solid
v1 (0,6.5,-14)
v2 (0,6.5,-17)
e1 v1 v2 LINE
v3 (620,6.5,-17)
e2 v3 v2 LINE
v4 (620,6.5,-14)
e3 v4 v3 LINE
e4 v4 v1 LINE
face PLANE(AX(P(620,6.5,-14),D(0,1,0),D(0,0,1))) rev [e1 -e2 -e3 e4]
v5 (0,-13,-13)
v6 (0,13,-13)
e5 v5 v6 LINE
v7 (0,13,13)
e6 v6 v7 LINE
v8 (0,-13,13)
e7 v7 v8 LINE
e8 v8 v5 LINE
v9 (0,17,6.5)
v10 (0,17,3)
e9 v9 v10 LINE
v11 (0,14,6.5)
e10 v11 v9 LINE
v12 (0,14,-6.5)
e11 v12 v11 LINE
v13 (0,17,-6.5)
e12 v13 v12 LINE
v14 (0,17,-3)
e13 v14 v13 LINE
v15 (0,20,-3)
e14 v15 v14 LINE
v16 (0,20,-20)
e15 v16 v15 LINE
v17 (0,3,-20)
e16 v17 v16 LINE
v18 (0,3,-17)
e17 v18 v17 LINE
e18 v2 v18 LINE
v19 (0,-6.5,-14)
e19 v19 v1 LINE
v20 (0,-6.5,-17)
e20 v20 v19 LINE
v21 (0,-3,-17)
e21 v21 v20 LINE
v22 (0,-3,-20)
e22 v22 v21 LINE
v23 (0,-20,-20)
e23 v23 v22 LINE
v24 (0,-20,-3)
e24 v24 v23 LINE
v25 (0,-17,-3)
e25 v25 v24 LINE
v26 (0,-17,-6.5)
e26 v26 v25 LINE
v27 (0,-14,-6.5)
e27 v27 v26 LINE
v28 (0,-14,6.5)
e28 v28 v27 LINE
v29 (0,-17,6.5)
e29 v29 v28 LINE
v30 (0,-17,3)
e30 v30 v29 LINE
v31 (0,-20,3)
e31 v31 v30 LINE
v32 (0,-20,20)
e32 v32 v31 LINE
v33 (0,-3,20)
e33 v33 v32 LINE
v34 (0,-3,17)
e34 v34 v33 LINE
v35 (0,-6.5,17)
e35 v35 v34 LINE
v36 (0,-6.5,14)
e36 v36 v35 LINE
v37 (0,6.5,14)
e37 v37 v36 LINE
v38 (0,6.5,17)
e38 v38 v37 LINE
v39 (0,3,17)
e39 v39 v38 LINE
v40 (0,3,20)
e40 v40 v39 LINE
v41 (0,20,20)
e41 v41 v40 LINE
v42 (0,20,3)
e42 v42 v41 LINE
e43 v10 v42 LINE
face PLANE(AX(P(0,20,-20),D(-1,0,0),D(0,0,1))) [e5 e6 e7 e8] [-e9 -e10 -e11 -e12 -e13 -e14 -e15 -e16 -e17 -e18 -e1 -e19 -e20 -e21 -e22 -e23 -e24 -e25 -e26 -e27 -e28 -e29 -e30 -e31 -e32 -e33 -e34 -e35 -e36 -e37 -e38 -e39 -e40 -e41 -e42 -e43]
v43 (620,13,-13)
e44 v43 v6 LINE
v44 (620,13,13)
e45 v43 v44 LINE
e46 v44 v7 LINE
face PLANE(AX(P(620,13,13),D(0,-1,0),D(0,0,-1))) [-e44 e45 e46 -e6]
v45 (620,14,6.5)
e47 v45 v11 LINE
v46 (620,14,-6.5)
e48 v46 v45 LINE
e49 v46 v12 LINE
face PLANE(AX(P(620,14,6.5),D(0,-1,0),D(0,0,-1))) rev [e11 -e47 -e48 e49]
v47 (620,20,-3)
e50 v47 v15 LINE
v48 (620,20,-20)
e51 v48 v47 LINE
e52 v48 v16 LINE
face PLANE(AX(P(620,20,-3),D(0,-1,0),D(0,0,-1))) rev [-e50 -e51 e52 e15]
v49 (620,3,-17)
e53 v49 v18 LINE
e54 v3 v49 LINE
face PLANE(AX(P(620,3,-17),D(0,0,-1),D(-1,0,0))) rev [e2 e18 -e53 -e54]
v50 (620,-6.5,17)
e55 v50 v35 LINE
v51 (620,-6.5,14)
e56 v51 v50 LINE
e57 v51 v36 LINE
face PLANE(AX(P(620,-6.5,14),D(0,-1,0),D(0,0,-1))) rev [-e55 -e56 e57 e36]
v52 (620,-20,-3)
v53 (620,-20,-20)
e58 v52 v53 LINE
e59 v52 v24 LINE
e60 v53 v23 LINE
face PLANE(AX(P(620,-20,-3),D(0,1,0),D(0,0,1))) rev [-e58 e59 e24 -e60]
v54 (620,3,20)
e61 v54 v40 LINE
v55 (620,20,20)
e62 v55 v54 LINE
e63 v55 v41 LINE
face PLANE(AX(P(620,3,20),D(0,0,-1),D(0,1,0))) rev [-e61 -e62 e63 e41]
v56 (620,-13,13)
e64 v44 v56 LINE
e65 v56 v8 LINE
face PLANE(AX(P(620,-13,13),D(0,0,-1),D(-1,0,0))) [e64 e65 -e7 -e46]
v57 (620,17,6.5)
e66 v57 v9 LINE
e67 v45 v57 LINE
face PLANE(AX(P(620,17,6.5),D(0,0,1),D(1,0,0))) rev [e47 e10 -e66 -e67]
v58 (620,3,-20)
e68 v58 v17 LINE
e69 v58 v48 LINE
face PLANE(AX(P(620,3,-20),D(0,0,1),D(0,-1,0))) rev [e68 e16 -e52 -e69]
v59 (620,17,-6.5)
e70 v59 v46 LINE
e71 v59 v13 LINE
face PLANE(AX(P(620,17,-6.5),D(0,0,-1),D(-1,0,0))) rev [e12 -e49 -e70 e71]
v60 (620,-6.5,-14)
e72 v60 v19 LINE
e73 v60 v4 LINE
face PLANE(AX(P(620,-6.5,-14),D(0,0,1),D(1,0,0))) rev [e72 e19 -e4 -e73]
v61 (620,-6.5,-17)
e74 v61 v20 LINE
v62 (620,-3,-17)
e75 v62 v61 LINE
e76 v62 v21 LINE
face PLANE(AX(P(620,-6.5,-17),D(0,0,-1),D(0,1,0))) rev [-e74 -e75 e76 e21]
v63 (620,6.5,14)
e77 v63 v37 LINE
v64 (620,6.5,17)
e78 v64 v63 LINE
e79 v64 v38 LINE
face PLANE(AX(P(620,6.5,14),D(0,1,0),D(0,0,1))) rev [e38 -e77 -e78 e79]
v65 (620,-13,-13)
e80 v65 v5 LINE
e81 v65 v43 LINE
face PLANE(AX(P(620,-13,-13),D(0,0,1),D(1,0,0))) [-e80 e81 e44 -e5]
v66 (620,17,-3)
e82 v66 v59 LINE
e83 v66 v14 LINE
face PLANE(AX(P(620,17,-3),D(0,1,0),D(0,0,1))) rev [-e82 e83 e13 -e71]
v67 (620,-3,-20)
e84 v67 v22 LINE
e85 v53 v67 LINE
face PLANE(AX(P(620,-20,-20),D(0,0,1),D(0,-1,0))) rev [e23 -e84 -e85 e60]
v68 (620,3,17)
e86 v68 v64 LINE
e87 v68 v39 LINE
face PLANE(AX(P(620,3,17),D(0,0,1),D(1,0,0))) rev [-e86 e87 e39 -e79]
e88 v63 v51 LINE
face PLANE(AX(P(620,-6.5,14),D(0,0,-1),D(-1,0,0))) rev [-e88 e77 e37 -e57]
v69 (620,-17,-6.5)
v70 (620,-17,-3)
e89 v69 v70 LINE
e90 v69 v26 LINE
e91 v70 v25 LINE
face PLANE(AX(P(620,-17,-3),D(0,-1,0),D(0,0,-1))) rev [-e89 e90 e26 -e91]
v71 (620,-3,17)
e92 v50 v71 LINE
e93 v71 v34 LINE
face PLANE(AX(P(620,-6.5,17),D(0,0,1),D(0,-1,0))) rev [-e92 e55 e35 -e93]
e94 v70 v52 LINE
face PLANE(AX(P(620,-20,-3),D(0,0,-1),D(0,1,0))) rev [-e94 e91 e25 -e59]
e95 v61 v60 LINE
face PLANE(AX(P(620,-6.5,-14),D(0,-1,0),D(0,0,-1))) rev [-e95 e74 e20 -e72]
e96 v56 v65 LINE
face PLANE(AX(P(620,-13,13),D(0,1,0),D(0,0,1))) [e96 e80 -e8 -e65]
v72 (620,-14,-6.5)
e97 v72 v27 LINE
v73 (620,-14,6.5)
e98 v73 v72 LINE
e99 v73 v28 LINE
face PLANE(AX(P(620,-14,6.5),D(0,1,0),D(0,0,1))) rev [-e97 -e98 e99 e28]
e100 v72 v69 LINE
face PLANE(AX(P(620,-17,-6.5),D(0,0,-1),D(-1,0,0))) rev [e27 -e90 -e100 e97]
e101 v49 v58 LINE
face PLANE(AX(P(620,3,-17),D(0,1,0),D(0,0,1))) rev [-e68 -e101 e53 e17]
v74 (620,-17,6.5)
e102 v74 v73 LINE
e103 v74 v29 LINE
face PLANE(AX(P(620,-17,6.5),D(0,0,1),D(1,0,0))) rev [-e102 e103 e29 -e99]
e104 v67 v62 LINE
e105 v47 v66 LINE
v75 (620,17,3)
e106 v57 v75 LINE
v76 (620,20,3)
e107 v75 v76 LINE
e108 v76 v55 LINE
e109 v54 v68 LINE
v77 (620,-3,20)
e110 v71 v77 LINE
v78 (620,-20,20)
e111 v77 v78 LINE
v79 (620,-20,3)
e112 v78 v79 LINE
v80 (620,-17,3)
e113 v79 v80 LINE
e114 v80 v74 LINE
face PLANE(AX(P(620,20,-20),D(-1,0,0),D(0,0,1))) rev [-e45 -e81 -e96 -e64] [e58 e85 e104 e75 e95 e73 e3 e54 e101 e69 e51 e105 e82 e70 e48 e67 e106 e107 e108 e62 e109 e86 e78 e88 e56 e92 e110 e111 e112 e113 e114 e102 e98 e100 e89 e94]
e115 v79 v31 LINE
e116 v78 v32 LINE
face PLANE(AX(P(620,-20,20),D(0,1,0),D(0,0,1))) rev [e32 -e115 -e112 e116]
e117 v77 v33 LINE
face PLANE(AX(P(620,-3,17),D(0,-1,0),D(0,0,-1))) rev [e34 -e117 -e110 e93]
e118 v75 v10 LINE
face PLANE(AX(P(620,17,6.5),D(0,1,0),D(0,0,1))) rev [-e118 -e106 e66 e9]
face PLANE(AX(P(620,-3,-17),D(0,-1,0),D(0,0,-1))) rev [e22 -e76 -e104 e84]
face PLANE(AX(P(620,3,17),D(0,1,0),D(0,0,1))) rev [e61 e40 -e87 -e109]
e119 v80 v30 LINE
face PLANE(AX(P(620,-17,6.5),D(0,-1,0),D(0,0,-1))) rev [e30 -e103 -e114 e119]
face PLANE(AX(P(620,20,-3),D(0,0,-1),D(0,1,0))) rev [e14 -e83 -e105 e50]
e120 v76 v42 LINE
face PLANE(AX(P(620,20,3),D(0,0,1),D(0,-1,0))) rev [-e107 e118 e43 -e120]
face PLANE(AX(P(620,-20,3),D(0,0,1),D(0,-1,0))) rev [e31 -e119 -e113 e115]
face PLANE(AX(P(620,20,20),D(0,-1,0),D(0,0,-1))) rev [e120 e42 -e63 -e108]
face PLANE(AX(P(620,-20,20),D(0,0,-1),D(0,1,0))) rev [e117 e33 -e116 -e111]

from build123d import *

# Parameters (mm, degrees)
SKETCH1_W           = 26
SKETCH1_H           = 26
BOSS_EXTRUDE1_DEPTH = 620


with BuildPart() as part:
    # Sketch1 → Boss-Extrude1 (new body)
    with BuildSketch(Plane(origin=(0, 0, 0), x_dir=(0, 0, -1), z_dir=(1, 0, 0))):
        Polygon((-20, -20), (-3, -20), (-3, -17), (-6.5, -17), (-6.5, -14), (6.5, -14), (6.5, -17), (3, -17), (3, -20), (20, -20), (20, -3), (17, -3), (17, -6.5), (14, -6.5), (14, 6.5), (17, 6.5), (17, 3), (20, 3), (20, 20), (3, 20), (3, 17), (6.5, 17), (6.5, 14), (-6.5, 14), (-6.5, 17), (-3, 17), (-3, 20), (-20, 20), (-20, 3), (-17, 3), (-17, 6.5), (-14, 6.5), (-14, -6.5), (-17, -6.5), (-17, -3), (-20, -3), align=None)
        Rectangle(SKETCH1_W, SKETCH1_H, mode=Mode.SUBTRACT)
    extrude(amount=BOSS_EXTRUDE1_DEPTH)


solid = part.part
